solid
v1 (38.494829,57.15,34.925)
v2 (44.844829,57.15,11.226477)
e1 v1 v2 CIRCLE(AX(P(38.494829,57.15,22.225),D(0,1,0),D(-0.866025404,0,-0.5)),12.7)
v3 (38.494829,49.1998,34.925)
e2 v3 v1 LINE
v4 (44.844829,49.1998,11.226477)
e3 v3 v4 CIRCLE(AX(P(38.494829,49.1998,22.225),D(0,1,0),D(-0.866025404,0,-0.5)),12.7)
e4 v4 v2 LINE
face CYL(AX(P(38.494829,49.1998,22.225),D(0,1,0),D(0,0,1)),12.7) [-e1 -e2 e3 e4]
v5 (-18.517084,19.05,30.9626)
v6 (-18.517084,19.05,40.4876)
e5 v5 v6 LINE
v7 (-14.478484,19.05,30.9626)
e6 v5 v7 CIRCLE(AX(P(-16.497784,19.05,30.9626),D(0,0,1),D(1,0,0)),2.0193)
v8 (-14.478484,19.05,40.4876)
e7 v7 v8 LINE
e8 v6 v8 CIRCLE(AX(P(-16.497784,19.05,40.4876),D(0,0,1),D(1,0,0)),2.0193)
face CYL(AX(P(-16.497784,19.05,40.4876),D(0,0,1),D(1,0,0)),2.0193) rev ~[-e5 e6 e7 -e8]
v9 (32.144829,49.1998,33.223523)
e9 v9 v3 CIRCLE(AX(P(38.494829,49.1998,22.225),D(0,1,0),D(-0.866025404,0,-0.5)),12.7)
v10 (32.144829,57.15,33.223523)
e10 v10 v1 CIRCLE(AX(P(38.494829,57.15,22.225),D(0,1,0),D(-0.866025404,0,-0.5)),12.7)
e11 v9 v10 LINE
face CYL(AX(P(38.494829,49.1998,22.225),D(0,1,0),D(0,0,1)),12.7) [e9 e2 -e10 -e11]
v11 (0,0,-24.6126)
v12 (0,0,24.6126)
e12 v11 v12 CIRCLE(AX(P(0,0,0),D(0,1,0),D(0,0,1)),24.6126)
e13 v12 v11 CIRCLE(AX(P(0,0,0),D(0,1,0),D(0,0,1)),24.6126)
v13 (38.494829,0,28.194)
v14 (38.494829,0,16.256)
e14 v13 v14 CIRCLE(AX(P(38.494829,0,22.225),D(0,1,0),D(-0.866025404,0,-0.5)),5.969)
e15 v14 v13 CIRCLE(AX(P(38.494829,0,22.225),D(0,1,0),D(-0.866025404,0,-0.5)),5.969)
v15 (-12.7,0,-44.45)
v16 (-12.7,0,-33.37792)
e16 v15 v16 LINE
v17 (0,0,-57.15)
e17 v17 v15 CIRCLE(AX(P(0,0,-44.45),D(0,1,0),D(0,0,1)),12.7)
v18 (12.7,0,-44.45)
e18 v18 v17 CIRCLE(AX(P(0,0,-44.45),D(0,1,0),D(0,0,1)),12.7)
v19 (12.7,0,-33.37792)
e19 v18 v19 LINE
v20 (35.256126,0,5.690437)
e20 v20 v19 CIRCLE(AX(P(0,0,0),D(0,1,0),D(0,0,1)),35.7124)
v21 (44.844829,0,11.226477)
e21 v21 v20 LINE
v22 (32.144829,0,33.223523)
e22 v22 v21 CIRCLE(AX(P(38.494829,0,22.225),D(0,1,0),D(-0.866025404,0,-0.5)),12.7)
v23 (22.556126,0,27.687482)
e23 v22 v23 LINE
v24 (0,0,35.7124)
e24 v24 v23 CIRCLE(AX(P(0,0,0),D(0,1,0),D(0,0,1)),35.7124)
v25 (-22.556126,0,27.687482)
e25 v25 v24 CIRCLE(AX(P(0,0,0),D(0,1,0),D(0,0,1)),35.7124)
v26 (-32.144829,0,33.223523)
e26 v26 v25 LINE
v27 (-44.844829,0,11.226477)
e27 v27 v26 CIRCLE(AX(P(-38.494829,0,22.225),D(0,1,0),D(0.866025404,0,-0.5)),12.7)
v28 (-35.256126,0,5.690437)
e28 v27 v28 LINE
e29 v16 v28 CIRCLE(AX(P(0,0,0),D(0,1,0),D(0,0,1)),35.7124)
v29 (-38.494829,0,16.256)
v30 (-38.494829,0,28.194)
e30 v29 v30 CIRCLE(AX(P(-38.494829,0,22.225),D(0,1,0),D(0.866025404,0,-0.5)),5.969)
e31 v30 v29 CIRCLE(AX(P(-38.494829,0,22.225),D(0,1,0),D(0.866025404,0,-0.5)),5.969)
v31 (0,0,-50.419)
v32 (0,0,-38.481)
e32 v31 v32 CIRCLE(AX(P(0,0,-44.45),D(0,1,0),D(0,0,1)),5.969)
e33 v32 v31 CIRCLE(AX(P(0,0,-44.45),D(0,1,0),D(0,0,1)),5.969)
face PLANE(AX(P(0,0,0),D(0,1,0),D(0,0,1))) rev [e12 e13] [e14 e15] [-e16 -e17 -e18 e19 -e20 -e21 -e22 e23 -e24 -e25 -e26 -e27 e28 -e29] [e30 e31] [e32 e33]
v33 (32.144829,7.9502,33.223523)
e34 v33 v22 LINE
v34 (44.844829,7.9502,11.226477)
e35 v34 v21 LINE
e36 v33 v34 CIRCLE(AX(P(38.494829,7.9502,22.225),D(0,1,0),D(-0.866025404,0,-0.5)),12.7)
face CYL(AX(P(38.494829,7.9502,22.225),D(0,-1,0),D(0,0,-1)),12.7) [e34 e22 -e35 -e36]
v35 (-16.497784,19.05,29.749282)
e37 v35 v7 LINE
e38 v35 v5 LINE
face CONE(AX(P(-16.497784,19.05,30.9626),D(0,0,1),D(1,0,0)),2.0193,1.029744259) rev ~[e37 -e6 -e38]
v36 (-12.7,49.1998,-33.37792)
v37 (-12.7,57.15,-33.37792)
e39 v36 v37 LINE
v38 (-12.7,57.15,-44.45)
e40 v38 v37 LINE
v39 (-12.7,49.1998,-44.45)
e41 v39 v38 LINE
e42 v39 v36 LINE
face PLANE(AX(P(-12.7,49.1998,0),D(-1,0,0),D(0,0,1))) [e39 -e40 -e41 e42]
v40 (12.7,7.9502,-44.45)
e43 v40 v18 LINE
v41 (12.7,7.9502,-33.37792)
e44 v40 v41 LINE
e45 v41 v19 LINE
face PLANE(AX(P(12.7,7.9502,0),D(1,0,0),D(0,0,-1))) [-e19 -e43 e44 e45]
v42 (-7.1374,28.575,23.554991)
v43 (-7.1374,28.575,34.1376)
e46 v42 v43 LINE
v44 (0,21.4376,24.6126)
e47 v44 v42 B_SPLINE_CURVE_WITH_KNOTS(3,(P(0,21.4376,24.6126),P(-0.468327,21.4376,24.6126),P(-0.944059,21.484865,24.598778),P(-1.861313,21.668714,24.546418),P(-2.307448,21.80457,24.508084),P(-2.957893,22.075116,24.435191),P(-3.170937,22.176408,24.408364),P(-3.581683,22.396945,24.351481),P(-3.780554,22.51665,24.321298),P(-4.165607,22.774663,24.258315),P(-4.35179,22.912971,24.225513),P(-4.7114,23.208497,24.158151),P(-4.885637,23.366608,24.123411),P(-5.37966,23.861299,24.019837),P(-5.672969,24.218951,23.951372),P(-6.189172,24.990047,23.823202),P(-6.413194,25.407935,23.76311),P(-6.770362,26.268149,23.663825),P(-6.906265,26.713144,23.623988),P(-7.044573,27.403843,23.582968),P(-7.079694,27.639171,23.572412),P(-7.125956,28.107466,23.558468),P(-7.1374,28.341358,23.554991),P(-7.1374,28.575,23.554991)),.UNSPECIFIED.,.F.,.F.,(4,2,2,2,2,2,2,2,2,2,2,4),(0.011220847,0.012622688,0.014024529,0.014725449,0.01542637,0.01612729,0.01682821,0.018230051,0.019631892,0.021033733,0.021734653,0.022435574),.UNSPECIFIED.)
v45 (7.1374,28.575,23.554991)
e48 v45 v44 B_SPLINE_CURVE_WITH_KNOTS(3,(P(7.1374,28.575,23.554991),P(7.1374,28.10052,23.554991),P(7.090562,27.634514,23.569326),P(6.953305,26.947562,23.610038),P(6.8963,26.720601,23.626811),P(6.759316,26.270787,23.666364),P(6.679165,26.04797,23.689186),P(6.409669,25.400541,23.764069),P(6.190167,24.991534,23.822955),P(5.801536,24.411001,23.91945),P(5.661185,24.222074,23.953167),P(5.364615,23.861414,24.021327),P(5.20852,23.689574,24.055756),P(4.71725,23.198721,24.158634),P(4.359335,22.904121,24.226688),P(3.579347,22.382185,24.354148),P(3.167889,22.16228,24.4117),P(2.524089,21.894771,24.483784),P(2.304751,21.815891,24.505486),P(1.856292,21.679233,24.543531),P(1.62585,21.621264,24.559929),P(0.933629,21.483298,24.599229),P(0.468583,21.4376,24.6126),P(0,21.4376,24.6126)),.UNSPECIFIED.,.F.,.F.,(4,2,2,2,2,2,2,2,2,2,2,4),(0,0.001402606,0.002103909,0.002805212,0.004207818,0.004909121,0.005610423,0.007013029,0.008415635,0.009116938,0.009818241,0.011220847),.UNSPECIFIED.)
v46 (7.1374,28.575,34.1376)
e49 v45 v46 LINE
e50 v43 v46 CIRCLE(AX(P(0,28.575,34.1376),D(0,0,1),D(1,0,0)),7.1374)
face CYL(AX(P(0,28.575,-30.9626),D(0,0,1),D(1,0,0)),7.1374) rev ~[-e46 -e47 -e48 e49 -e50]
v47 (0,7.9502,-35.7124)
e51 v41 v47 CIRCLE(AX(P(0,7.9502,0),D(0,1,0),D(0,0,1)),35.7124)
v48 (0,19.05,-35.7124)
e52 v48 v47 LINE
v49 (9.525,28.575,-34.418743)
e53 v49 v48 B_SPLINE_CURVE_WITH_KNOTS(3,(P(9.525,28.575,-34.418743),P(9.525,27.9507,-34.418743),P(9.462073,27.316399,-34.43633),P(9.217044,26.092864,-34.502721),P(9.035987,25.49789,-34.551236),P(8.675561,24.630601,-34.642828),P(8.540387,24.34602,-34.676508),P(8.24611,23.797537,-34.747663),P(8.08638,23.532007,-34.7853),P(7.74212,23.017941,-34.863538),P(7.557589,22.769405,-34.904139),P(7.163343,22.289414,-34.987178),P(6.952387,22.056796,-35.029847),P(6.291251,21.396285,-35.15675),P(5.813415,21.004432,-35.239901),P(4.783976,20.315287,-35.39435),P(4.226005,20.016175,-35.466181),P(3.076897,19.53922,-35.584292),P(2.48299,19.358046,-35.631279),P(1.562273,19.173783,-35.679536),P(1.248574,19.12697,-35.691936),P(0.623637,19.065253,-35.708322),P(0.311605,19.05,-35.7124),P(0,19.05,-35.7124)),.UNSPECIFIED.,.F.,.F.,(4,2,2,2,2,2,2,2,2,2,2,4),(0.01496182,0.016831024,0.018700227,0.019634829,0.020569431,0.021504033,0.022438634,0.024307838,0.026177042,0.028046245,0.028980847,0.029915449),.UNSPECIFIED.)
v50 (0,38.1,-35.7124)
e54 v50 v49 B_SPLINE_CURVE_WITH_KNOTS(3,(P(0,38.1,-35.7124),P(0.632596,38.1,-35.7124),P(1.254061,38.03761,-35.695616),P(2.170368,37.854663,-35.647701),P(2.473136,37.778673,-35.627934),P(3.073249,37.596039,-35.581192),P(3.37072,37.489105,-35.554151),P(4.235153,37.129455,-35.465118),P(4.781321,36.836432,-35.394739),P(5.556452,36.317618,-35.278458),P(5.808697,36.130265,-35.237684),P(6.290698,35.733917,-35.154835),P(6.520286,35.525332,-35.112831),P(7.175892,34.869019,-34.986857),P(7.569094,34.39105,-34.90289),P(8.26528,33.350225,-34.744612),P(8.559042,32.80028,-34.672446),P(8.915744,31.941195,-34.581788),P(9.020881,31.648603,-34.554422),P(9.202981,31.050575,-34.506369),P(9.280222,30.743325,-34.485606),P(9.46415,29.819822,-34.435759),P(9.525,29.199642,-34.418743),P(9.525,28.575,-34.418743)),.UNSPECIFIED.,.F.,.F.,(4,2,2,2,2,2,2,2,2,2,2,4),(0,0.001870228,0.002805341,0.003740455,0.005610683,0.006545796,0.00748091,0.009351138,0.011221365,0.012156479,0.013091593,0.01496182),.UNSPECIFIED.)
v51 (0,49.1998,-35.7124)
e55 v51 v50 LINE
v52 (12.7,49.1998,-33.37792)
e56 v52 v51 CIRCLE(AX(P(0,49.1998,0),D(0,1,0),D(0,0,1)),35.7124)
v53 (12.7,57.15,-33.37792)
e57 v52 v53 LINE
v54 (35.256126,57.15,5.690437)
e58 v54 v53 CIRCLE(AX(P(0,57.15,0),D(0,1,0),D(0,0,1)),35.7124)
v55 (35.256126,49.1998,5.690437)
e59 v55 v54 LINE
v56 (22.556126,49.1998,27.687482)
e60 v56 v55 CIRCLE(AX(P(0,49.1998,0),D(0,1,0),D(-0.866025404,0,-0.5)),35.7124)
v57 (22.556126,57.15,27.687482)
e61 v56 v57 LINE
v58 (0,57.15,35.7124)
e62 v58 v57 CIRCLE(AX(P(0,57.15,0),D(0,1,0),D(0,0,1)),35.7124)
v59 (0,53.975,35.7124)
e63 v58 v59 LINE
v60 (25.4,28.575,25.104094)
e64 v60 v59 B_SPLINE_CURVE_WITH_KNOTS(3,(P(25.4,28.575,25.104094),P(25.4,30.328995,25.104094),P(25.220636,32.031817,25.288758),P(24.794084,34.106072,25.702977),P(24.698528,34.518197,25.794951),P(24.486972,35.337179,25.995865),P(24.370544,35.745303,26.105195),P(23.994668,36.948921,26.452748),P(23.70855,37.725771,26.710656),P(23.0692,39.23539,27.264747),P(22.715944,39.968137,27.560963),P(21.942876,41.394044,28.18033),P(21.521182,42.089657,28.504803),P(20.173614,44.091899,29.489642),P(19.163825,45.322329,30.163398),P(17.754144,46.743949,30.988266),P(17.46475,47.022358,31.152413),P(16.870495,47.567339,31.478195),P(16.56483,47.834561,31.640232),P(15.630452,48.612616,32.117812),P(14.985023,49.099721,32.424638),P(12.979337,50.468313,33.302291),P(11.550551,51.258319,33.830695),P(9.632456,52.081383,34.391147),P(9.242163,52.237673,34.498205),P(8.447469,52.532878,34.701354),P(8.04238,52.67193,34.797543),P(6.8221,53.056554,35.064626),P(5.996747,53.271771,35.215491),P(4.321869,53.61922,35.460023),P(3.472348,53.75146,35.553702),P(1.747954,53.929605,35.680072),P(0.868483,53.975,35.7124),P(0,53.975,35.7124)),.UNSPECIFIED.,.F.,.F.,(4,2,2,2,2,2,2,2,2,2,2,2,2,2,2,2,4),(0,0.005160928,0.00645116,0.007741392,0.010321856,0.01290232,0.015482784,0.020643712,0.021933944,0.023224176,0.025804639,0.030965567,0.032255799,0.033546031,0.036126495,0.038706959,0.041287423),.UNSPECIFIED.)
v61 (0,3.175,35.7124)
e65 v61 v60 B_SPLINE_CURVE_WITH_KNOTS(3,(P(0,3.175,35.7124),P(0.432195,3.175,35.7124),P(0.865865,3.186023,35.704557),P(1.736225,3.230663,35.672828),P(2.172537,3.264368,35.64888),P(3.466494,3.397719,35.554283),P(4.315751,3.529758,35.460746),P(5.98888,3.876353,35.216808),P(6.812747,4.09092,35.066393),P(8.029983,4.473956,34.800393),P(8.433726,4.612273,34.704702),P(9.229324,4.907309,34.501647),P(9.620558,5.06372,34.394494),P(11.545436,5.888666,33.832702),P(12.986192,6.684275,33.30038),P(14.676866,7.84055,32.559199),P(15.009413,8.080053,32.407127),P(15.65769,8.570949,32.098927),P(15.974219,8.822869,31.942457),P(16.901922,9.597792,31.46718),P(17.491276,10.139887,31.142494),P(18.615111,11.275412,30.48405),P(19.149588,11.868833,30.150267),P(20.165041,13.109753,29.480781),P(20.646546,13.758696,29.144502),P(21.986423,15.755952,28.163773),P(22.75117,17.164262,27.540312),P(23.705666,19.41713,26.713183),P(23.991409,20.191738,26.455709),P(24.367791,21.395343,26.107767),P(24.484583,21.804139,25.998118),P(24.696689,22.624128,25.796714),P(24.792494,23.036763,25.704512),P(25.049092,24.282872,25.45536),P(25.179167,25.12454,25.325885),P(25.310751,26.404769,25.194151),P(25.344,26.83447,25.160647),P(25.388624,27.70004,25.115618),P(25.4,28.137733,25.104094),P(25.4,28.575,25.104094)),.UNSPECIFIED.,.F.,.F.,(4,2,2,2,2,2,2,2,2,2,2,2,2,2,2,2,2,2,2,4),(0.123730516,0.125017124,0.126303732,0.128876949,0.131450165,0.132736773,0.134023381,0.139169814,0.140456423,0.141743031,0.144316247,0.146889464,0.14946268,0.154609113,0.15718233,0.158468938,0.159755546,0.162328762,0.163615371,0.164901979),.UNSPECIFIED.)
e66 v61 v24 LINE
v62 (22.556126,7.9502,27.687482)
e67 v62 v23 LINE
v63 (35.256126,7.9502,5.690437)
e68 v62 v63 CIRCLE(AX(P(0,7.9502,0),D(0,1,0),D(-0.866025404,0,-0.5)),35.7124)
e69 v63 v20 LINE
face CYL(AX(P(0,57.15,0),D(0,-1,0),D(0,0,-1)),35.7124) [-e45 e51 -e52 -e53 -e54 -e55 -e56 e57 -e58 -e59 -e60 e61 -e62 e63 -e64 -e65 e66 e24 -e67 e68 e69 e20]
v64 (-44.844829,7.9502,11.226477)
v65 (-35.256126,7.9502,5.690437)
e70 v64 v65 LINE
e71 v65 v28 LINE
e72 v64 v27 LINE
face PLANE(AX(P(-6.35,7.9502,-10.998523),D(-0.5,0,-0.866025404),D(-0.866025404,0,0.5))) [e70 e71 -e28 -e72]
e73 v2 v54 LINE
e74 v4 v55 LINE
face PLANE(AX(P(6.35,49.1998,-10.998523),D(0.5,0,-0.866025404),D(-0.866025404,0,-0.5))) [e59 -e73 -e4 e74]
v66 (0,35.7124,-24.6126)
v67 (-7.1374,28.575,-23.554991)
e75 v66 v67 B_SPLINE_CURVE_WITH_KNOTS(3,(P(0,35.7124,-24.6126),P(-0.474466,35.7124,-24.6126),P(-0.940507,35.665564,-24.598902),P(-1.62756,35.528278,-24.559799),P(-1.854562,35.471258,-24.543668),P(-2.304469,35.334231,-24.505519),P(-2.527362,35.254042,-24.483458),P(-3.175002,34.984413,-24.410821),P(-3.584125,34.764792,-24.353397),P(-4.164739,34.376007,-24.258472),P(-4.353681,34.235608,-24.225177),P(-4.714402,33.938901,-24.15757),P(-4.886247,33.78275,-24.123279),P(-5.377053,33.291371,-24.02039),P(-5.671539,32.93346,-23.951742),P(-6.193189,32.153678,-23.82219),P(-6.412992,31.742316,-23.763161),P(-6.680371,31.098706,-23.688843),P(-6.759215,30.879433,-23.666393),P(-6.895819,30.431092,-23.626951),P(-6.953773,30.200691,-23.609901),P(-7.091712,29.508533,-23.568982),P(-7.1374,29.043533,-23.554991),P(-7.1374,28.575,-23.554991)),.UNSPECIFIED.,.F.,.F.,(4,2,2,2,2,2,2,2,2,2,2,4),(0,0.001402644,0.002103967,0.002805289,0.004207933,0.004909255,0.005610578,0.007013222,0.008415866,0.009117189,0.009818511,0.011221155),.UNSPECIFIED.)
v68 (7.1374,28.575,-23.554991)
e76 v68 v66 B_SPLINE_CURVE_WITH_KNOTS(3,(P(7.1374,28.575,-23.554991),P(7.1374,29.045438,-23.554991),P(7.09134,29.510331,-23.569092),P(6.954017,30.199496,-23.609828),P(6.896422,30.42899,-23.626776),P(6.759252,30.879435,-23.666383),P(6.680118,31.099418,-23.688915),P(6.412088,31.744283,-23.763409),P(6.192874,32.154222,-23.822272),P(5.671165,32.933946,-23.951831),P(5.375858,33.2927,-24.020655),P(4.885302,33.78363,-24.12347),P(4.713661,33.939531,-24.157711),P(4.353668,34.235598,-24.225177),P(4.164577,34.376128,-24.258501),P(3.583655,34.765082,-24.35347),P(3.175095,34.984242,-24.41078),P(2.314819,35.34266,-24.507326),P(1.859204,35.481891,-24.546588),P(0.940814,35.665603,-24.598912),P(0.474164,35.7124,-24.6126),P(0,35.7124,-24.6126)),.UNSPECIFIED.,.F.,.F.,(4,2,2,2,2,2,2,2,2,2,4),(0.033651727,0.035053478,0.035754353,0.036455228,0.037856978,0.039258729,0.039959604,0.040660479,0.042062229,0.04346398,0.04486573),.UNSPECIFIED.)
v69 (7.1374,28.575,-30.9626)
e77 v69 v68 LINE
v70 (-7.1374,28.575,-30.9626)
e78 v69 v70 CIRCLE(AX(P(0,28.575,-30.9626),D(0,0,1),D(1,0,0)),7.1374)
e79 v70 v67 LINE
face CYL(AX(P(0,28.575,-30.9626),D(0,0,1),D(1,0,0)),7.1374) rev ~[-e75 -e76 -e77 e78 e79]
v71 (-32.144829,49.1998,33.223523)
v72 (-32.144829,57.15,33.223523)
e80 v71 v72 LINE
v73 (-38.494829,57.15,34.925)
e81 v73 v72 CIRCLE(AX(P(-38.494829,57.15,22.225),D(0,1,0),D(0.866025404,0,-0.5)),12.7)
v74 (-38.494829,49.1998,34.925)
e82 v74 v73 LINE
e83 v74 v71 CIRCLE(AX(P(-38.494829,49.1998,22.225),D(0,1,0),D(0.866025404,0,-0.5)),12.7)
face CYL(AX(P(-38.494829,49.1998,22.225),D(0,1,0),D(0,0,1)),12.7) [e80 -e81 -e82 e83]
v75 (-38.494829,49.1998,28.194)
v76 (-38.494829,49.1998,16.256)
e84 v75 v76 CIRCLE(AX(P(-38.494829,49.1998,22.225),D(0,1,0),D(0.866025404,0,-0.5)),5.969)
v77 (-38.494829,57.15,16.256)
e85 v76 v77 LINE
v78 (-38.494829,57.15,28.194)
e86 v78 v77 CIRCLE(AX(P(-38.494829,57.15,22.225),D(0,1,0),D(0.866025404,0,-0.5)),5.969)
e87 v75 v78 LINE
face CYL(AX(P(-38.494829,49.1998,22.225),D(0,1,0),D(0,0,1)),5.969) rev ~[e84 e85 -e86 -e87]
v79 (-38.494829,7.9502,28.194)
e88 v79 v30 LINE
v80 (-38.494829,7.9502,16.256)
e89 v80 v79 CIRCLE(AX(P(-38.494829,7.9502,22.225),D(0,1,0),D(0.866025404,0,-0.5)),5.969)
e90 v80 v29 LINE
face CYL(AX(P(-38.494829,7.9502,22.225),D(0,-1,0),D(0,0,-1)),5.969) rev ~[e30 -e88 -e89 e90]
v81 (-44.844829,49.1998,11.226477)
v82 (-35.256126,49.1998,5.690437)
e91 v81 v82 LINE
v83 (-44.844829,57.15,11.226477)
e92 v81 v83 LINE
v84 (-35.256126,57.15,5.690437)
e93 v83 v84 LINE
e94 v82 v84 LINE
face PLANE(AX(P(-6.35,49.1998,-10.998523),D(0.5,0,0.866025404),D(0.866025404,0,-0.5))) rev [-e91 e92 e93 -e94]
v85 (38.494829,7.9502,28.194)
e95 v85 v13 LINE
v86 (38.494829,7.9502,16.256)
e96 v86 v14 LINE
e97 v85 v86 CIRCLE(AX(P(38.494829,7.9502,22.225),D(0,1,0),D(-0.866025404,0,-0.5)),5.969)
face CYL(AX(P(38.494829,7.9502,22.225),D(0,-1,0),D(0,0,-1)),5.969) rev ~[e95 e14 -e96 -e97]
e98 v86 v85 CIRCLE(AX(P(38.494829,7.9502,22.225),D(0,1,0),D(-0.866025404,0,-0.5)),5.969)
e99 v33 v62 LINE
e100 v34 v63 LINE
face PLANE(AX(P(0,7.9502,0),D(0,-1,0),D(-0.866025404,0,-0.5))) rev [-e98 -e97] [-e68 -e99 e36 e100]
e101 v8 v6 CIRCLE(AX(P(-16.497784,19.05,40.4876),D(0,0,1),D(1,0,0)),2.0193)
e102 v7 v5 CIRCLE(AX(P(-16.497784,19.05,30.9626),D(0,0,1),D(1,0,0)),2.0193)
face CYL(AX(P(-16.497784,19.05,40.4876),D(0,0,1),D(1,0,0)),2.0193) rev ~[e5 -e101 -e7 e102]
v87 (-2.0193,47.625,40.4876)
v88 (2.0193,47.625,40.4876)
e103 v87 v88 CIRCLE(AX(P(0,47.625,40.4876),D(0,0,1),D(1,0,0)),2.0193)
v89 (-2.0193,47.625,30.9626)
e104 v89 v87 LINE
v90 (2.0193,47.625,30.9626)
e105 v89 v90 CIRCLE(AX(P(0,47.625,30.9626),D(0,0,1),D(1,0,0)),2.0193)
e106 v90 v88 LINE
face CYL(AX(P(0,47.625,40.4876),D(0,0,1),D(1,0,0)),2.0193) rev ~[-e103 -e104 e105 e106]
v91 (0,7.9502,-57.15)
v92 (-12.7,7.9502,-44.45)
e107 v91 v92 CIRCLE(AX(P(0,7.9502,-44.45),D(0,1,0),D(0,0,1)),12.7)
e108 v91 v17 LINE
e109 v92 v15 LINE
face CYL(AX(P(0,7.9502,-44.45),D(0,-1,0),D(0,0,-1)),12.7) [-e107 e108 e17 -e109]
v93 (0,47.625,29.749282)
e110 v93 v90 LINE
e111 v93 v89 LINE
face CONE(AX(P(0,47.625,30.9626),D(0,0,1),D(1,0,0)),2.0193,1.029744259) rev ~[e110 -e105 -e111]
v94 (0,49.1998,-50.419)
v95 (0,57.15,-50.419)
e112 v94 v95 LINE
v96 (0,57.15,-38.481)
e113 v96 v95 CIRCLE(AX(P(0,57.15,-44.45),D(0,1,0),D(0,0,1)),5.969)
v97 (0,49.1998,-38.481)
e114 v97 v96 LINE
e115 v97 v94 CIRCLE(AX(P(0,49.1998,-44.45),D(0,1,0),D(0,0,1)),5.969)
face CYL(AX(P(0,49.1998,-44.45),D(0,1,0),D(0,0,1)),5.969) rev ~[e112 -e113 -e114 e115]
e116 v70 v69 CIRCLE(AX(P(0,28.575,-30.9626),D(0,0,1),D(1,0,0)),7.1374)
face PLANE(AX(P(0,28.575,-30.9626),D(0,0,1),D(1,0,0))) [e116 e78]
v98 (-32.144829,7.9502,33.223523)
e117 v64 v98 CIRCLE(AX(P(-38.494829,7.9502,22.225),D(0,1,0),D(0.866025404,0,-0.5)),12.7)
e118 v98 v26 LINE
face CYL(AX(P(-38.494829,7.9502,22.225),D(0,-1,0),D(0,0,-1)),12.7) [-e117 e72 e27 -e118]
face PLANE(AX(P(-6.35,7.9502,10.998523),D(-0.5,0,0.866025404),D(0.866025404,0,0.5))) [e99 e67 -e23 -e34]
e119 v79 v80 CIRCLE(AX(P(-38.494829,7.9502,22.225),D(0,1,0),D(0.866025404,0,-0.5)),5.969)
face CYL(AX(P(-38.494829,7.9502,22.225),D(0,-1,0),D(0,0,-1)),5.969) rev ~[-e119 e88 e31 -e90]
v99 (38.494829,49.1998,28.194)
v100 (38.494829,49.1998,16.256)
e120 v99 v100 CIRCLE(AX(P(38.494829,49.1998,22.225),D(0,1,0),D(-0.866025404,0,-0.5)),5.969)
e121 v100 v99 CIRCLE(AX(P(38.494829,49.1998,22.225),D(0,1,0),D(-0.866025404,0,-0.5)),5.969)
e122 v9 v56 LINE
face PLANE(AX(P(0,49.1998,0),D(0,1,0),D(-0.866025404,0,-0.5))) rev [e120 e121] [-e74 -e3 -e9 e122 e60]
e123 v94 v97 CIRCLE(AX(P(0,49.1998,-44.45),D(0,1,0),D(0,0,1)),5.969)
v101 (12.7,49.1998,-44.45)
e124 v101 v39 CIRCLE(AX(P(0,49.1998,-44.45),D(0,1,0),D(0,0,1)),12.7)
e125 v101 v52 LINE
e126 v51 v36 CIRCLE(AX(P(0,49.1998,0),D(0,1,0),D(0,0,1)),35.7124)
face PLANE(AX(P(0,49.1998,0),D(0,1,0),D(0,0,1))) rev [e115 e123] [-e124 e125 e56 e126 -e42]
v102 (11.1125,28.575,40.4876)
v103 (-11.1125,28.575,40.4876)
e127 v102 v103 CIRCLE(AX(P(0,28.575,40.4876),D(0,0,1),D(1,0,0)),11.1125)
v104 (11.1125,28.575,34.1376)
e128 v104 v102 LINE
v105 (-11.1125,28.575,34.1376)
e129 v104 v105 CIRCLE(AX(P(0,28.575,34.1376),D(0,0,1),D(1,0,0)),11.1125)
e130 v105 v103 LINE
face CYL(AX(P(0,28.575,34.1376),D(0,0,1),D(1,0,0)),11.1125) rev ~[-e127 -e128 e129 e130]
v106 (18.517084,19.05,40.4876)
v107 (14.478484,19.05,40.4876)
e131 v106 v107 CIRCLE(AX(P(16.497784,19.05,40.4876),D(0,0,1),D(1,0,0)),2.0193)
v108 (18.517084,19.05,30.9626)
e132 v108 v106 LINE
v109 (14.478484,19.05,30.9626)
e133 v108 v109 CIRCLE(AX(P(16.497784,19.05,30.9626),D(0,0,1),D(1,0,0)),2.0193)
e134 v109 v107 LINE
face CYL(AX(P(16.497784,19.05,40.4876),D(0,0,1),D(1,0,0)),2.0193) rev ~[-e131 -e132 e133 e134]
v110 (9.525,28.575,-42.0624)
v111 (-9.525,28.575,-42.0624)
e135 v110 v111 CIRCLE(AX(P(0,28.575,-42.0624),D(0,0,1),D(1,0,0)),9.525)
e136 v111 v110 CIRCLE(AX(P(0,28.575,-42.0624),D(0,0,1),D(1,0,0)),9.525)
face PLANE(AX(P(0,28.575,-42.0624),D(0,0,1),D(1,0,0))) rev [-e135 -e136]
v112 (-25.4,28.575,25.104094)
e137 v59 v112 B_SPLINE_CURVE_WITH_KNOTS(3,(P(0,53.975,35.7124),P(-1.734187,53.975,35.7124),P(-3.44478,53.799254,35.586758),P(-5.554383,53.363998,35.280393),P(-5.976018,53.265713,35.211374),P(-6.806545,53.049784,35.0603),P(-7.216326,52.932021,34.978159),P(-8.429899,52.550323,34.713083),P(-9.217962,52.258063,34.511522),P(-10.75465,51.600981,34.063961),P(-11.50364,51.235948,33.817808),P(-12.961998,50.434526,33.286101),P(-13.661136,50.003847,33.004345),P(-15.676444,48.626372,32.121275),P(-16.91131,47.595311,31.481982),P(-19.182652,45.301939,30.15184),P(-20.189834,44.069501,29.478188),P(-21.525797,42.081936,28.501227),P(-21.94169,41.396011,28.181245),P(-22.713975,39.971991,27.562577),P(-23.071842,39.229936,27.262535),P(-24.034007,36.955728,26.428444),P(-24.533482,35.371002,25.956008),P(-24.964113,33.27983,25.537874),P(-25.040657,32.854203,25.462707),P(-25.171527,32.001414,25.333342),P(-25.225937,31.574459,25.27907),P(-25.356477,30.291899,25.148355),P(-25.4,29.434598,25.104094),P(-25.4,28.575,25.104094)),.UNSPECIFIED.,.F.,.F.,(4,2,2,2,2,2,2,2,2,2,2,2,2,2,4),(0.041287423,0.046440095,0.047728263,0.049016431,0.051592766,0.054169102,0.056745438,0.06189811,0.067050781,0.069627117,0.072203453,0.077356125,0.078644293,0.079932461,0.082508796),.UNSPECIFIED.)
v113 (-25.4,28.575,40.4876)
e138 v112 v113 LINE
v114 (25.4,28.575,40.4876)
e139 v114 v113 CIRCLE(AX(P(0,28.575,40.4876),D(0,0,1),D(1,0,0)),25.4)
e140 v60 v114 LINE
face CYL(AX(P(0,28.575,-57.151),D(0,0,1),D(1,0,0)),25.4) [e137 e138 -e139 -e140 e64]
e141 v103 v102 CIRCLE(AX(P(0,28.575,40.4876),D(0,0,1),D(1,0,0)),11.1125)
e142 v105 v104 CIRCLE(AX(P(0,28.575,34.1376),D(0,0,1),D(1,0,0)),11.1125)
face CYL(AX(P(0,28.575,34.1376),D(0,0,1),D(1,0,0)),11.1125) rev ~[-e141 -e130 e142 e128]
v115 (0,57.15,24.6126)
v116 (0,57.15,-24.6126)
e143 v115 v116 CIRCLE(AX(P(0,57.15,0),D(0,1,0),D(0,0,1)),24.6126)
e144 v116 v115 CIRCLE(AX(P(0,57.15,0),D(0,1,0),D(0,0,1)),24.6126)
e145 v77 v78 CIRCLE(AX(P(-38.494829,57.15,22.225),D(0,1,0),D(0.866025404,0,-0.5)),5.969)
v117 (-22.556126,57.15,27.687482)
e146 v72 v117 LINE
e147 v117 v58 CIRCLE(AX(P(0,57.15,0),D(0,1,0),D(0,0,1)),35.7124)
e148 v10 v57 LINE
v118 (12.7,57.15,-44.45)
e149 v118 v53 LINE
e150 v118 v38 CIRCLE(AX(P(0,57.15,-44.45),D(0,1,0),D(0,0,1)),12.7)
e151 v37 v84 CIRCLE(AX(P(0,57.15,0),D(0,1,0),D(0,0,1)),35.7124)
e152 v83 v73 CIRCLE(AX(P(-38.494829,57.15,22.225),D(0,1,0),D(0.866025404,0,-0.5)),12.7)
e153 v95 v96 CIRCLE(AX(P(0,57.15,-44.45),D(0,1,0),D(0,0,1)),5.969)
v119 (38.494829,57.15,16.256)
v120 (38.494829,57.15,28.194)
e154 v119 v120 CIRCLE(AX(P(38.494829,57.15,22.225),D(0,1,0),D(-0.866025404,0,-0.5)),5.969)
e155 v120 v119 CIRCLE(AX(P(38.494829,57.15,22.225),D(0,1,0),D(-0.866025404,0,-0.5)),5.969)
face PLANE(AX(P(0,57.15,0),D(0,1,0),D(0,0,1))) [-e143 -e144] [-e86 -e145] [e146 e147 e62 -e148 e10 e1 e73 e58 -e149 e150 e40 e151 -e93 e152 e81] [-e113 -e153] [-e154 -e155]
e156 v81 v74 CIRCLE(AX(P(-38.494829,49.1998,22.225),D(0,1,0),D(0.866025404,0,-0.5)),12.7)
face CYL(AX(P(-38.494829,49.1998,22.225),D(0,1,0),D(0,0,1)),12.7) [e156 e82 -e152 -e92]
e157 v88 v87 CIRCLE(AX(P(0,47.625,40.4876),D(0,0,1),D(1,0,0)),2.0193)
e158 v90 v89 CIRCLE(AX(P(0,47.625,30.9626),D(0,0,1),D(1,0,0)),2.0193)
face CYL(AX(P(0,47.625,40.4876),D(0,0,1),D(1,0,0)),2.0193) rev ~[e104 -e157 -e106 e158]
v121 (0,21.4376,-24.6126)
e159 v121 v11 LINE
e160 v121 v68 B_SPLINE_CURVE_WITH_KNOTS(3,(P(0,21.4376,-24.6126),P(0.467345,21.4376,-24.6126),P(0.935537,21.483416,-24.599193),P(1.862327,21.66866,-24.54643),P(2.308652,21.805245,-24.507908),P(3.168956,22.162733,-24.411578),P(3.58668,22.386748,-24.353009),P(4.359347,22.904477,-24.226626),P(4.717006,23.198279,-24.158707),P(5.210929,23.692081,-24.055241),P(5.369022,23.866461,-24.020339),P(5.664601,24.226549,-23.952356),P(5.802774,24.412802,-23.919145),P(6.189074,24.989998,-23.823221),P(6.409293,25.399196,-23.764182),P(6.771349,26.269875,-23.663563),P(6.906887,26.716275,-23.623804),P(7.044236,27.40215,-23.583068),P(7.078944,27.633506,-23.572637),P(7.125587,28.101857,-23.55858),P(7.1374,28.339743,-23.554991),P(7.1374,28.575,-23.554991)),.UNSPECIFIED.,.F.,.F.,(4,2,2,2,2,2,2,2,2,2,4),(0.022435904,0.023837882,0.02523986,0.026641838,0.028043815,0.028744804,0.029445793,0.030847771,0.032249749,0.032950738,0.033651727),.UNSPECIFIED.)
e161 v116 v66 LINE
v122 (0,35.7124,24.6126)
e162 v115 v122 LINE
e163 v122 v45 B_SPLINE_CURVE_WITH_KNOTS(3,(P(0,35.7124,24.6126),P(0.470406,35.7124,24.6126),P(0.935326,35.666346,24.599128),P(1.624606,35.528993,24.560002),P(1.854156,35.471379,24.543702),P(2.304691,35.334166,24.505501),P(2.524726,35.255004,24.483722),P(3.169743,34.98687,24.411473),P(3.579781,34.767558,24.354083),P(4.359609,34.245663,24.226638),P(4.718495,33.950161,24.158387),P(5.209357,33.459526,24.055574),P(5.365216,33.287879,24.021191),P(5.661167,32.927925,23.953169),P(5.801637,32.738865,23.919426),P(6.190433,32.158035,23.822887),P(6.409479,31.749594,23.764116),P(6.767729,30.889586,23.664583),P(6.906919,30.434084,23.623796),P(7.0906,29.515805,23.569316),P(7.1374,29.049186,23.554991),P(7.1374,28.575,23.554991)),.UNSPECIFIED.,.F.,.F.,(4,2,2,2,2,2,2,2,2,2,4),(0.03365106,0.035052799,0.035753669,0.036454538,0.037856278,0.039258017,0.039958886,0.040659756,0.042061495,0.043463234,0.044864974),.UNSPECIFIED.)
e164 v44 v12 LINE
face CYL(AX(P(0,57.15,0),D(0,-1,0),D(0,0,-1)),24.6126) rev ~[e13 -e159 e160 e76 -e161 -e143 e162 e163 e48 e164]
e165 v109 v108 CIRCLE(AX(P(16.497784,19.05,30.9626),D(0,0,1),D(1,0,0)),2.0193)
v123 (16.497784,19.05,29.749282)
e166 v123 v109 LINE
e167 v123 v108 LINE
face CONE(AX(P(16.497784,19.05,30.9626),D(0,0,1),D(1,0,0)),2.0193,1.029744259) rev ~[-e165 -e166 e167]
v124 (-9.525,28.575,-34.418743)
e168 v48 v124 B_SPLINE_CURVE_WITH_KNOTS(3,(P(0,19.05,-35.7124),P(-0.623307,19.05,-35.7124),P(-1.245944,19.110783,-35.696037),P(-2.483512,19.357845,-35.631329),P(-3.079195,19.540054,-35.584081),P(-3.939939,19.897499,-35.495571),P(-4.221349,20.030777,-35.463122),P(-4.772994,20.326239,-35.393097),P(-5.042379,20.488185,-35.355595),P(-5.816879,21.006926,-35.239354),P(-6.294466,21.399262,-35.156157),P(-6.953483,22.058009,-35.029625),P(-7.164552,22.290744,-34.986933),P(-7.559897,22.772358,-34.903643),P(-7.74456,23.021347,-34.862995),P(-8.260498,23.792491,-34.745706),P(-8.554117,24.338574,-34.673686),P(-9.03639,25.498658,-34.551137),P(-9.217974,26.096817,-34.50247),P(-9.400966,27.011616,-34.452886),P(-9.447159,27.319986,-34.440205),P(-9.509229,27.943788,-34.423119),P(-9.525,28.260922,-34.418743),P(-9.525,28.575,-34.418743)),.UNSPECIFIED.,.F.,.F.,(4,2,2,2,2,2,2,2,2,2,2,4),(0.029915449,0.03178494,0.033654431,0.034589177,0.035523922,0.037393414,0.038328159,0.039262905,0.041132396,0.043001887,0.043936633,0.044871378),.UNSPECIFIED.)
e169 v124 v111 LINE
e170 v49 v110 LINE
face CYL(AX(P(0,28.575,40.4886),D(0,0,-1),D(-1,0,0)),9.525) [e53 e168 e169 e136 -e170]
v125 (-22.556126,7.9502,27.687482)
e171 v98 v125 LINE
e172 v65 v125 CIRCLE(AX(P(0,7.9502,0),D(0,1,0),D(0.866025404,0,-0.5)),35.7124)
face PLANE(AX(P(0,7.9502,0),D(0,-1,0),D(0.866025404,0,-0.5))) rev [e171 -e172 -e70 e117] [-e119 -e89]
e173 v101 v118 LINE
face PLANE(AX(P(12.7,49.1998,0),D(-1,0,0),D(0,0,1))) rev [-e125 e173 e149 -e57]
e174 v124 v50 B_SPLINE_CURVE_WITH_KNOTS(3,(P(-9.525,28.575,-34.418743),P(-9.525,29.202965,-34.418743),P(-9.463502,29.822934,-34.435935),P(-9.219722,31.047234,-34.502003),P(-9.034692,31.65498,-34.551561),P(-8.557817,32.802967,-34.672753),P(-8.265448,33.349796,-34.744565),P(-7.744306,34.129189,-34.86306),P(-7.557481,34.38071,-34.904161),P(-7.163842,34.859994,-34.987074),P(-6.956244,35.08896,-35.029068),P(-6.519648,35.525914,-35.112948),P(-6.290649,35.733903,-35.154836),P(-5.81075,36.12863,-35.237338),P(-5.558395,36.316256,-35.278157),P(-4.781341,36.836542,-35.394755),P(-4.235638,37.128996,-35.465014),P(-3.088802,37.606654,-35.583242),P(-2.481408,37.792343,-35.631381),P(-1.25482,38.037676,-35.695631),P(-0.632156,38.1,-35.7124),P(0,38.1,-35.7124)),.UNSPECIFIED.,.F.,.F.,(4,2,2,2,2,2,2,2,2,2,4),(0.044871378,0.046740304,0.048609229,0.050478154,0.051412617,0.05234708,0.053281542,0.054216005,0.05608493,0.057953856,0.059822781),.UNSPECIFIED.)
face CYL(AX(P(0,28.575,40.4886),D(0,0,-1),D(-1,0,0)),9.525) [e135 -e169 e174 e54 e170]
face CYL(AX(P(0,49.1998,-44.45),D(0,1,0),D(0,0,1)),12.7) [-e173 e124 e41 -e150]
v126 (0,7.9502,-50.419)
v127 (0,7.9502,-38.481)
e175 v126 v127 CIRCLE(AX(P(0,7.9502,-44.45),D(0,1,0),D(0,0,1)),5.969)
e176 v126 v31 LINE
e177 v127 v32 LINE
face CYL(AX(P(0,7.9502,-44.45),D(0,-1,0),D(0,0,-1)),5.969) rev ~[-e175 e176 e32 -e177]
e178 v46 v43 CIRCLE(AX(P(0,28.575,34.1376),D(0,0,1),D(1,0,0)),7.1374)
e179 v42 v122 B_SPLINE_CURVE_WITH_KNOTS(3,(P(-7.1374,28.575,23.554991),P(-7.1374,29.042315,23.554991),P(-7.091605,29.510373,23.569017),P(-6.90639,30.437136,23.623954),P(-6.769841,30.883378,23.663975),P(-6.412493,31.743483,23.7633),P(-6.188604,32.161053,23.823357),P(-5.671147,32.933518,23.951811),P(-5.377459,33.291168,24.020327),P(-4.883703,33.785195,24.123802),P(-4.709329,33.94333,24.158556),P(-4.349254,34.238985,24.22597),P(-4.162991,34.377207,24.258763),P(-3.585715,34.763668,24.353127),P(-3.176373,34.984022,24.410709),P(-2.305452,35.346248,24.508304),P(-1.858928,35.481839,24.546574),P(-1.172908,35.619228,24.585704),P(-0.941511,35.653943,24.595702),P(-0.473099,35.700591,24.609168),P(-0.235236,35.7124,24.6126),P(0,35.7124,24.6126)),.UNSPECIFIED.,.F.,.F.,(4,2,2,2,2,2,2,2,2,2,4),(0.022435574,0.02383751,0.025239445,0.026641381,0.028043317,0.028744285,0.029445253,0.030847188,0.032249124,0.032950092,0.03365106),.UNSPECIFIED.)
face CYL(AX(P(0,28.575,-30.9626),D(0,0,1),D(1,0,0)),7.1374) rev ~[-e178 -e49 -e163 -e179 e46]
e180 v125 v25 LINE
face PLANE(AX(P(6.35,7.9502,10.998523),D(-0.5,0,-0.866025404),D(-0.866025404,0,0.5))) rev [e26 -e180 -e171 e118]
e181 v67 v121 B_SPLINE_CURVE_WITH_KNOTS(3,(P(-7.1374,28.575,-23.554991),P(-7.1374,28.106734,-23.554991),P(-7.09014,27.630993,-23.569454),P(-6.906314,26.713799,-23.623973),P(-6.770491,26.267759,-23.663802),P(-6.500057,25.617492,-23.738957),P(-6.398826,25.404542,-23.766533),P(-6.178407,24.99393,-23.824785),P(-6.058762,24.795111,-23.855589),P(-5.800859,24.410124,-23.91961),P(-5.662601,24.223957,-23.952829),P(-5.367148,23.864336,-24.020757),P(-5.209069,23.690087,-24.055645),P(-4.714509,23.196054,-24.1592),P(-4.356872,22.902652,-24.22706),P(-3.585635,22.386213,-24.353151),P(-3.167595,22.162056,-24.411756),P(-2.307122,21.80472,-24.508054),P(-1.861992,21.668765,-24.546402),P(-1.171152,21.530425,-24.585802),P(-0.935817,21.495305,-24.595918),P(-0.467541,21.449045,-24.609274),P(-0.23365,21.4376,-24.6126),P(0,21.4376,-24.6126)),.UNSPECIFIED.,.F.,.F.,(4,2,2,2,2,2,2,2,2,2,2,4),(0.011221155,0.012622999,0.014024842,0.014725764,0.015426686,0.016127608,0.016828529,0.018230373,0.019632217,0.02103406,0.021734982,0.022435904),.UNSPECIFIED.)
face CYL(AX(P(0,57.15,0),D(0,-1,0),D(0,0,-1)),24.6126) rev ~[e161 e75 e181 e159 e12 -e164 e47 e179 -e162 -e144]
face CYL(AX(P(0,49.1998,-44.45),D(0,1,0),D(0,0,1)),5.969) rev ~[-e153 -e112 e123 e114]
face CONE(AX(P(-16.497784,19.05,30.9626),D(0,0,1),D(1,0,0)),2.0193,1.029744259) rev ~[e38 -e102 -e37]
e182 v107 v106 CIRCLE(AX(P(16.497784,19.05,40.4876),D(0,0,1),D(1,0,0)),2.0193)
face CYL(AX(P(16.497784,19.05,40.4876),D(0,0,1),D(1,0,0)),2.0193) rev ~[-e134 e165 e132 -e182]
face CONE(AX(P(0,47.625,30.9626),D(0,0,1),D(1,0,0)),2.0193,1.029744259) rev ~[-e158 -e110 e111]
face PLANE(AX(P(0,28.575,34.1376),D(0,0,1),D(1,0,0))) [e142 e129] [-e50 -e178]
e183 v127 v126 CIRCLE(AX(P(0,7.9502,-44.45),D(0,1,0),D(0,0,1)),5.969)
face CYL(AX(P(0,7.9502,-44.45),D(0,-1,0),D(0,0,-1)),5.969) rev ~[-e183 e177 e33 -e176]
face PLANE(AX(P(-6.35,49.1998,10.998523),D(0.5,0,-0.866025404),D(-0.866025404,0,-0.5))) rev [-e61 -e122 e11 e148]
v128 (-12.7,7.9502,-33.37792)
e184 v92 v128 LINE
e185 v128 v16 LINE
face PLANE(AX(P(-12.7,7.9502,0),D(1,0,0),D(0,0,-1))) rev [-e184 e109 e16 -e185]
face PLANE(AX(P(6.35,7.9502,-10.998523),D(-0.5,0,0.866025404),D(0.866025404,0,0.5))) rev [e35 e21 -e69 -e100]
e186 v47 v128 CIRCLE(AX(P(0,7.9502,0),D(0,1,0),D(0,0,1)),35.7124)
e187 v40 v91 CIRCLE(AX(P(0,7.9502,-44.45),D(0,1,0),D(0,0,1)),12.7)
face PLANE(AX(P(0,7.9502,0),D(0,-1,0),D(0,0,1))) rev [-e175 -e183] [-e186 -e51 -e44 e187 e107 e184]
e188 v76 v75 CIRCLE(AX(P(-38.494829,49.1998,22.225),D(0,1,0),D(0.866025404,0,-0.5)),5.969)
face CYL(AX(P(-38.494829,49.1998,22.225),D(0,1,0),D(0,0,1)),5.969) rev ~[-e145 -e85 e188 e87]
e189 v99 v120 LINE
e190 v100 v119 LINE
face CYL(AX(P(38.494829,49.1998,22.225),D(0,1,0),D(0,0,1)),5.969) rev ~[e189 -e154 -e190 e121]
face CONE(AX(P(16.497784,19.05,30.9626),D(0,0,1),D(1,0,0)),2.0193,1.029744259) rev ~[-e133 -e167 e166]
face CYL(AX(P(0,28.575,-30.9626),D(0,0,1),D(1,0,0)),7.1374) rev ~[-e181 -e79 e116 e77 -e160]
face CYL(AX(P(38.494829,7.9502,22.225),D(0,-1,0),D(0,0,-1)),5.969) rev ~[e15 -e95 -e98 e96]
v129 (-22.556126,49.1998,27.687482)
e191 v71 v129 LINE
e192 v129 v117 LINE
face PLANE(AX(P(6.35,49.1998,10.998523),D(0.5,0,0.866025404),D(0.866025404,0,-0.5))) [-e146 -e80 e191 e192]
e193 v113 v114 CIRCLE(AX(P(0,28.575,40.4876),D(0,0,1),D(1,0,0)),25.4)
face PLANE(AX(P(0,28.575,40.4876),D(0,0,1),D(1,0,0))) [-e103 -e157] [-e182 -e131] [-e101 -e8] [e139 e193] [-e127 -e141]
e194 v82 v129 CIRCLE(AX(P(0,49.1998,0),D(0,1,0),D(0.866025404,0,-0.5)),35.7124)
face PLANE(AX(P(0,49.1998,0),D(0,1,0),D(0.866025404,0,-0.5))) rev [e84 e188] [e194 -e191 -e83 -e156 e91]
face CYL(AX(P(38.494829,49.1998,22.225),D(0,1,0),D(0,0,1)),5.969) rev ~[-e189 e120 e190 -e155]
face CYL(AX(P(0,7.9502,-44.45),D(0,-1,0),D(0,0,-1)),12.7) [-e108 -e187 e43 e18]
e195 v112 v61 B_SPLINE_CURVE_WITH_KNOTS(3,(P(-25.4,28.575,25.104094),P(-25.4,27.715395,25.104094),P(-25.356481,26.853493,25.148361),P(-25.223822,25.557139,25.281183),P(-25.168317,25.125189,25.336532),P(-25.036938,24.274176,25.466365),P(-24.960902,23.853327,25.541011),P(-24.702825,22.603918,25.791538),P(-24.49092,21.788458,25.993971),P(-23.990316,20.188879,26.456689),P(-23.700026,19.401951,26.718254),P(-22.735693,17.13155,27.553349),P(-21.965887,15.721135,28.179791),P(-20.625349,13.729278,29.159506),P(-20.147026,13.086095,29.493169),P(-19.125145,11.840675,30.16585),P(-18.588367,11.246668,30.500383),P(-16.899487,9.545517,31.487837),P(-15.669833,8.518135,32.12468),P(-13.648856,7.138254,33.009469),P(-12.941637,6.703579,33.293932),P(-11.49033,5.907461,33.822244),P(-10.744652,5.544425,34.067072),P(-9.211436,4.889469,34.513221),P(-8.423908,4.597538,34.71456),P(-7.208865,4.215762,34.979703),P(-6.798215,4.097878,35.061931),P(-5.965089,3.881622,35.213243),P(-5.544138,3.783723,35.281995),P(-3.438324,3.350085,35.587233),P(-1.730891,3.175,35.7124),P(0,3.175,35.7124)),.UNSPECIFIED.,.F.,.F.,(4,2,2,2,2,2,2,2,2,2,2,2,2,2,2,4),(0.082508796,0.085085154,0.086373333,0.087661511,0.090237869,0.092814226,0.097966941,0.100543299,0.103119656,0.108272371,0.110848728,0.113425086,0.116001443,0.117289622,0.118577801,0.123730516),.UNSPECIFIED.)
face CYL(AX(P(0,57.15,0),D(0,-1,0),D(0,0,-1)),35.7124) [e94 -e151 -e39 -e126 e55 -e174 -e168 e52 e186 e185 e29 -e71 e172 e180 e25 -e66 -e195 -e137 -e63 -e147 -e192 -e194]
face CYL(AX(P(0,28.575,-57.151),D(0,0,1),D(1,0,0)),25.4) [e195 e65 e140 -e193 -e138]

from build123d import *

# Parameters (mm, degrees)
SKETCH1_R                  = 35.7124
SKETCH1_R_2                = 24.6126
BOSS_EXTRUDE1_DEPTH        = 57.15
BOSS_EXTRUDE2_START        = -7.9502
SKETCH2_R                  = 5.969
BOSS_EXTRUDE2_DEPTH        = 7.9502
CIRPATTERN1_COUNT          = 3
MIRROR1_START              = -7.9502
MIRROR1_COPY_1_SKETCH_R    = 5.969
MIRROR1_COPY_1_DEPTH       = 7.9502
MIRROR1_COPY_2_SKETCH_R    = 5.969
MIRROR1_COPY_2_DEPTH       = 7.9502
BOSS_EXTRUDE3_REACH        = 126.178
BOSS_EXTRUDE3_END_RADIUS   = 35.7124
SKETCH3_R                  = 25.4
F_10_32_TAPPED_HOLE1_D     = 4.0386
F_10_32_TAPPED_HOLE1_DEPTH = 9.525
F_10_32_TAPPED_HOLE1_TIP   = 1.213317848
BOSS_EXTRUDE4_REACH        = 114.701
BOSS_EXTRUDE4_END_RADIUS   = 35.7124
SKETCH14_R                 = 9.525
SKETCH15_R                 = 11.1125
CUT_EXTRUDE1_DEPTH         = 6.35
SKETCH16_R                 = 7.1374
CUT_EXTRUDE2_DEPTH         = 71.4502


with BuildPart() as part:
    # Sketch1 → Boss-Extrude1 (new body)
    with BuildSketch(Plane(origin=(0, 0, 0), x_dir=(1, 0, 0), z_dir=(0, 1, 0))):
        with Locations(Location((0, 0, 0), (0, 0, 270))):
            Circle(SKETCH1_R)
        with Locations(Location((0, 0, 0), (0, 0, 270))):
            Circle(SKETCH1_R_2, mode=Mode.SUBTRACT)
    extrude(amount=BOSS_EXTRUDE1_DEPTH)

    # Sketch2 → Boss-Extrude2 (add)
    with BuildSketch(Plane(origin=(0, 57.15, 0), x_dir=(1, 0, 0), z_dir=(0, 1, 0)).offset(BOSS_EXTRUDE2_START)):
        with BuildLine():
            ThreePointArc((12.7, 44.45), (0, 57.15), (-12.7, 44.45))
            Line((-12.7, 44.45), (-12.7, 33.377919554))
            ThreePointArc((-12.7, 33.377919554), (0, 35.7124), (12.7, 33.377919554))
            Line((12.7, 33.377919554), (12.7, 44.45))
        make_face()
        with Locations(Location((0, 44.45, 0), (0, 0, 270))):
            Circle(SKETCH2_R, mode=Mode.SUBTRACT)
    boss_extrude2 = extrude(amount=BOSS_EXTRUDE2_DEPTH)

    # CirPattern1: Boss-Extrude2 ×3 about axis
    cirpattern1_axis = Axis((0, 0, 0), (0, 1, 0))
    for i in range(1, CIRPATTERN1_COUNT):
        add(boss_extrude2.rotate(cirpattern1_axis, i * 360 / CIRPATTERN1_COUNT))

    # Mirror1: Boss-Extrude2 across plane
    add(boss_extrude2.mirror(Plane.ZX.offset(28.575)))

    # Mirror1 copy 1 sketch → Mirror1 copy 1 (add)
    with BuildSketch(Plane(origin=(0, 0, 0), x_dir=(-0.4999999999999998, 0, -0.8660254037844387), z_dir=(0, -1, 0)).offset(MIRROR1_START)):
        with BuildLine():
            ThreePointArc((12.7, -44.45), (0, -57.15), (-12.7, -44.45))
            Line((-12.7, -44.45), (-12.7, -33.377919554))
            ThreePointArc((-12.7, -33.377919554), (0, -35.7124), (12.7, -33.377919554))
            Line((12.7, -33.377919554), (12.7, -44.45))
        make_face()
        with Locations((0, -44.45)):
            Circle(MIRROR1_COPY_1_SKETCH_R, mode=Mode.SUBTRACT)
    extrude(amount=MIRROR1_COPY_1_DEPTH)

    # Mirror1 copy 2 sketch → Mirror1 copy 2 (add)
    with BuildSketch(Plane(origin=(0, 0, 0), x_dir=(-0.5000000000000004, 0, 0.8660254037844384), z_dir=(0, -1, 0)).offset(MIRROR1_START)):
        with BuildLine():
            ThreePointArc((12.7, -44.45), (0, -57.15), (-12.7, -44.45))
            Line((-12.7, -44.45), (-12.7, -33.377919554))
            ThreePointArc((-12.7, -33.377919554), (0, -35.7124), (12.7, -33.377919554))
            Line((12.7, -33.377919554), (12.7, -44.45))
        make_face()
        with Locations((0, -44.45)):
            Circle(MIRROR1_COPY_2_SKETCH_R, mode=Mode.SUBTRACT)
    extrude(amount=MIRROR1_COPY_2_DEPTH)

    # Boss-Extrude3: up to this cylinder (the profile starts outside it)
    boss_extrude3_end = Plane(origin=(0, 28.575, 0), z_dir=(0, -1, 0)) * Cylinder(BOSS_EXTRUDE3_END_RADIUS, 324.7808, mode=Mode.PRIVATE)
    # Sketch3 → Boss-Extrude3 (add, up to the surface)
    with BuildSketch(Plane.XY.offset(40.4876), mode=Mode.PRIVATE) as boss_extrude3_sk1:
        with Locations((0, 28.575)):
            Circle(SKETCH3_R)
    boss_extrude3_tool1 = extrude(boss_extrude3_sk1.sketch, amount=-BOSS_EXTRUDE3_REACH, mode=Mode.PRIVATE) - boss_extrude3_end
    add(boss_extrude3_tool1.solids().sort_by_distance((0, 28.575, 40.4876))[0])

    # #10-32 Tapped Hole1
    with Locations(Plane.XY.offset(40.4876)):
        with Locations((0, 47.625), (16.497783942, 19.05), (-16.497783942, 19.05)):
            Hole(F_10_32_TAPPED_HOLE1_D / 2, depth=F_10_32_TAPPED_HOLE1_DEPTH)
            with Locations((0, 0, -(F_10_32_TAPPED_HOLE1_DEPTH + F_10_32_TAPPED_HOLE1_TIP / 2))):  # 118° drill point
                Cone(0, F_10_32_TAPPED_HOLE1_D / 2, F_10_32_TAPPED_HOLE1_TIP, mode=Mode.SUBTRACT)

    # Boss-Extrude4: up to this cylinder (the profile starts outside it)
    boss_extrude4_end = Plane(origin=(0, 28.575, 0), z_dir=(0, -1, 0)) * Cylinder(BOSS_EXTRUDE4_END_RADIUS, 301.8268, mode=Mode.PRIVATE)
    # Sketch14 → Boss-Extrude4 (add, up to the surface)
    with BuildSketch(Plane.XY.offset(-42.0624), mode=Mode.PRIVATE) as boss_extrude4_sk1:
        with Locations(Location((0, 28.575, 0), (0, 0, 90))):
            Circle(SKETCH14_R)
    boss_extrude4_tool1 = extrude(boss_extrude4_sk1.sketch, amount=BOSS_EXTRUDE4_REACH, mode=Mode.PRIVATE) - boss_extrude4_end
    add(boss_extrude4_tool1.solids().sort_by_distance((0, 28.575, -42.0624))[0])

    # Sketch15 → Cut-Extrude1 (cut)
    with BuildSketch(Plane.XY.offset(40.4876)):
        with Locations((0, 28.575)):
            Circle(SKETCH15_R)
    extrude(amount=-CUT_EXTRUDE1_DEPTH, mode=Mode.SUBTRACT)

    # Sketch16 → Cut-Extrude2 (cut)
    with BuildSketch(Plane.XY.offset(40.4876)):
        with Locations((0, 28.575)):
            Circle(SKETCH16_R)
    extrude(amount=-CUT_EXTRUDE2_DEPTH, mode=Mode.SUBTRACT)


solid = part.part
